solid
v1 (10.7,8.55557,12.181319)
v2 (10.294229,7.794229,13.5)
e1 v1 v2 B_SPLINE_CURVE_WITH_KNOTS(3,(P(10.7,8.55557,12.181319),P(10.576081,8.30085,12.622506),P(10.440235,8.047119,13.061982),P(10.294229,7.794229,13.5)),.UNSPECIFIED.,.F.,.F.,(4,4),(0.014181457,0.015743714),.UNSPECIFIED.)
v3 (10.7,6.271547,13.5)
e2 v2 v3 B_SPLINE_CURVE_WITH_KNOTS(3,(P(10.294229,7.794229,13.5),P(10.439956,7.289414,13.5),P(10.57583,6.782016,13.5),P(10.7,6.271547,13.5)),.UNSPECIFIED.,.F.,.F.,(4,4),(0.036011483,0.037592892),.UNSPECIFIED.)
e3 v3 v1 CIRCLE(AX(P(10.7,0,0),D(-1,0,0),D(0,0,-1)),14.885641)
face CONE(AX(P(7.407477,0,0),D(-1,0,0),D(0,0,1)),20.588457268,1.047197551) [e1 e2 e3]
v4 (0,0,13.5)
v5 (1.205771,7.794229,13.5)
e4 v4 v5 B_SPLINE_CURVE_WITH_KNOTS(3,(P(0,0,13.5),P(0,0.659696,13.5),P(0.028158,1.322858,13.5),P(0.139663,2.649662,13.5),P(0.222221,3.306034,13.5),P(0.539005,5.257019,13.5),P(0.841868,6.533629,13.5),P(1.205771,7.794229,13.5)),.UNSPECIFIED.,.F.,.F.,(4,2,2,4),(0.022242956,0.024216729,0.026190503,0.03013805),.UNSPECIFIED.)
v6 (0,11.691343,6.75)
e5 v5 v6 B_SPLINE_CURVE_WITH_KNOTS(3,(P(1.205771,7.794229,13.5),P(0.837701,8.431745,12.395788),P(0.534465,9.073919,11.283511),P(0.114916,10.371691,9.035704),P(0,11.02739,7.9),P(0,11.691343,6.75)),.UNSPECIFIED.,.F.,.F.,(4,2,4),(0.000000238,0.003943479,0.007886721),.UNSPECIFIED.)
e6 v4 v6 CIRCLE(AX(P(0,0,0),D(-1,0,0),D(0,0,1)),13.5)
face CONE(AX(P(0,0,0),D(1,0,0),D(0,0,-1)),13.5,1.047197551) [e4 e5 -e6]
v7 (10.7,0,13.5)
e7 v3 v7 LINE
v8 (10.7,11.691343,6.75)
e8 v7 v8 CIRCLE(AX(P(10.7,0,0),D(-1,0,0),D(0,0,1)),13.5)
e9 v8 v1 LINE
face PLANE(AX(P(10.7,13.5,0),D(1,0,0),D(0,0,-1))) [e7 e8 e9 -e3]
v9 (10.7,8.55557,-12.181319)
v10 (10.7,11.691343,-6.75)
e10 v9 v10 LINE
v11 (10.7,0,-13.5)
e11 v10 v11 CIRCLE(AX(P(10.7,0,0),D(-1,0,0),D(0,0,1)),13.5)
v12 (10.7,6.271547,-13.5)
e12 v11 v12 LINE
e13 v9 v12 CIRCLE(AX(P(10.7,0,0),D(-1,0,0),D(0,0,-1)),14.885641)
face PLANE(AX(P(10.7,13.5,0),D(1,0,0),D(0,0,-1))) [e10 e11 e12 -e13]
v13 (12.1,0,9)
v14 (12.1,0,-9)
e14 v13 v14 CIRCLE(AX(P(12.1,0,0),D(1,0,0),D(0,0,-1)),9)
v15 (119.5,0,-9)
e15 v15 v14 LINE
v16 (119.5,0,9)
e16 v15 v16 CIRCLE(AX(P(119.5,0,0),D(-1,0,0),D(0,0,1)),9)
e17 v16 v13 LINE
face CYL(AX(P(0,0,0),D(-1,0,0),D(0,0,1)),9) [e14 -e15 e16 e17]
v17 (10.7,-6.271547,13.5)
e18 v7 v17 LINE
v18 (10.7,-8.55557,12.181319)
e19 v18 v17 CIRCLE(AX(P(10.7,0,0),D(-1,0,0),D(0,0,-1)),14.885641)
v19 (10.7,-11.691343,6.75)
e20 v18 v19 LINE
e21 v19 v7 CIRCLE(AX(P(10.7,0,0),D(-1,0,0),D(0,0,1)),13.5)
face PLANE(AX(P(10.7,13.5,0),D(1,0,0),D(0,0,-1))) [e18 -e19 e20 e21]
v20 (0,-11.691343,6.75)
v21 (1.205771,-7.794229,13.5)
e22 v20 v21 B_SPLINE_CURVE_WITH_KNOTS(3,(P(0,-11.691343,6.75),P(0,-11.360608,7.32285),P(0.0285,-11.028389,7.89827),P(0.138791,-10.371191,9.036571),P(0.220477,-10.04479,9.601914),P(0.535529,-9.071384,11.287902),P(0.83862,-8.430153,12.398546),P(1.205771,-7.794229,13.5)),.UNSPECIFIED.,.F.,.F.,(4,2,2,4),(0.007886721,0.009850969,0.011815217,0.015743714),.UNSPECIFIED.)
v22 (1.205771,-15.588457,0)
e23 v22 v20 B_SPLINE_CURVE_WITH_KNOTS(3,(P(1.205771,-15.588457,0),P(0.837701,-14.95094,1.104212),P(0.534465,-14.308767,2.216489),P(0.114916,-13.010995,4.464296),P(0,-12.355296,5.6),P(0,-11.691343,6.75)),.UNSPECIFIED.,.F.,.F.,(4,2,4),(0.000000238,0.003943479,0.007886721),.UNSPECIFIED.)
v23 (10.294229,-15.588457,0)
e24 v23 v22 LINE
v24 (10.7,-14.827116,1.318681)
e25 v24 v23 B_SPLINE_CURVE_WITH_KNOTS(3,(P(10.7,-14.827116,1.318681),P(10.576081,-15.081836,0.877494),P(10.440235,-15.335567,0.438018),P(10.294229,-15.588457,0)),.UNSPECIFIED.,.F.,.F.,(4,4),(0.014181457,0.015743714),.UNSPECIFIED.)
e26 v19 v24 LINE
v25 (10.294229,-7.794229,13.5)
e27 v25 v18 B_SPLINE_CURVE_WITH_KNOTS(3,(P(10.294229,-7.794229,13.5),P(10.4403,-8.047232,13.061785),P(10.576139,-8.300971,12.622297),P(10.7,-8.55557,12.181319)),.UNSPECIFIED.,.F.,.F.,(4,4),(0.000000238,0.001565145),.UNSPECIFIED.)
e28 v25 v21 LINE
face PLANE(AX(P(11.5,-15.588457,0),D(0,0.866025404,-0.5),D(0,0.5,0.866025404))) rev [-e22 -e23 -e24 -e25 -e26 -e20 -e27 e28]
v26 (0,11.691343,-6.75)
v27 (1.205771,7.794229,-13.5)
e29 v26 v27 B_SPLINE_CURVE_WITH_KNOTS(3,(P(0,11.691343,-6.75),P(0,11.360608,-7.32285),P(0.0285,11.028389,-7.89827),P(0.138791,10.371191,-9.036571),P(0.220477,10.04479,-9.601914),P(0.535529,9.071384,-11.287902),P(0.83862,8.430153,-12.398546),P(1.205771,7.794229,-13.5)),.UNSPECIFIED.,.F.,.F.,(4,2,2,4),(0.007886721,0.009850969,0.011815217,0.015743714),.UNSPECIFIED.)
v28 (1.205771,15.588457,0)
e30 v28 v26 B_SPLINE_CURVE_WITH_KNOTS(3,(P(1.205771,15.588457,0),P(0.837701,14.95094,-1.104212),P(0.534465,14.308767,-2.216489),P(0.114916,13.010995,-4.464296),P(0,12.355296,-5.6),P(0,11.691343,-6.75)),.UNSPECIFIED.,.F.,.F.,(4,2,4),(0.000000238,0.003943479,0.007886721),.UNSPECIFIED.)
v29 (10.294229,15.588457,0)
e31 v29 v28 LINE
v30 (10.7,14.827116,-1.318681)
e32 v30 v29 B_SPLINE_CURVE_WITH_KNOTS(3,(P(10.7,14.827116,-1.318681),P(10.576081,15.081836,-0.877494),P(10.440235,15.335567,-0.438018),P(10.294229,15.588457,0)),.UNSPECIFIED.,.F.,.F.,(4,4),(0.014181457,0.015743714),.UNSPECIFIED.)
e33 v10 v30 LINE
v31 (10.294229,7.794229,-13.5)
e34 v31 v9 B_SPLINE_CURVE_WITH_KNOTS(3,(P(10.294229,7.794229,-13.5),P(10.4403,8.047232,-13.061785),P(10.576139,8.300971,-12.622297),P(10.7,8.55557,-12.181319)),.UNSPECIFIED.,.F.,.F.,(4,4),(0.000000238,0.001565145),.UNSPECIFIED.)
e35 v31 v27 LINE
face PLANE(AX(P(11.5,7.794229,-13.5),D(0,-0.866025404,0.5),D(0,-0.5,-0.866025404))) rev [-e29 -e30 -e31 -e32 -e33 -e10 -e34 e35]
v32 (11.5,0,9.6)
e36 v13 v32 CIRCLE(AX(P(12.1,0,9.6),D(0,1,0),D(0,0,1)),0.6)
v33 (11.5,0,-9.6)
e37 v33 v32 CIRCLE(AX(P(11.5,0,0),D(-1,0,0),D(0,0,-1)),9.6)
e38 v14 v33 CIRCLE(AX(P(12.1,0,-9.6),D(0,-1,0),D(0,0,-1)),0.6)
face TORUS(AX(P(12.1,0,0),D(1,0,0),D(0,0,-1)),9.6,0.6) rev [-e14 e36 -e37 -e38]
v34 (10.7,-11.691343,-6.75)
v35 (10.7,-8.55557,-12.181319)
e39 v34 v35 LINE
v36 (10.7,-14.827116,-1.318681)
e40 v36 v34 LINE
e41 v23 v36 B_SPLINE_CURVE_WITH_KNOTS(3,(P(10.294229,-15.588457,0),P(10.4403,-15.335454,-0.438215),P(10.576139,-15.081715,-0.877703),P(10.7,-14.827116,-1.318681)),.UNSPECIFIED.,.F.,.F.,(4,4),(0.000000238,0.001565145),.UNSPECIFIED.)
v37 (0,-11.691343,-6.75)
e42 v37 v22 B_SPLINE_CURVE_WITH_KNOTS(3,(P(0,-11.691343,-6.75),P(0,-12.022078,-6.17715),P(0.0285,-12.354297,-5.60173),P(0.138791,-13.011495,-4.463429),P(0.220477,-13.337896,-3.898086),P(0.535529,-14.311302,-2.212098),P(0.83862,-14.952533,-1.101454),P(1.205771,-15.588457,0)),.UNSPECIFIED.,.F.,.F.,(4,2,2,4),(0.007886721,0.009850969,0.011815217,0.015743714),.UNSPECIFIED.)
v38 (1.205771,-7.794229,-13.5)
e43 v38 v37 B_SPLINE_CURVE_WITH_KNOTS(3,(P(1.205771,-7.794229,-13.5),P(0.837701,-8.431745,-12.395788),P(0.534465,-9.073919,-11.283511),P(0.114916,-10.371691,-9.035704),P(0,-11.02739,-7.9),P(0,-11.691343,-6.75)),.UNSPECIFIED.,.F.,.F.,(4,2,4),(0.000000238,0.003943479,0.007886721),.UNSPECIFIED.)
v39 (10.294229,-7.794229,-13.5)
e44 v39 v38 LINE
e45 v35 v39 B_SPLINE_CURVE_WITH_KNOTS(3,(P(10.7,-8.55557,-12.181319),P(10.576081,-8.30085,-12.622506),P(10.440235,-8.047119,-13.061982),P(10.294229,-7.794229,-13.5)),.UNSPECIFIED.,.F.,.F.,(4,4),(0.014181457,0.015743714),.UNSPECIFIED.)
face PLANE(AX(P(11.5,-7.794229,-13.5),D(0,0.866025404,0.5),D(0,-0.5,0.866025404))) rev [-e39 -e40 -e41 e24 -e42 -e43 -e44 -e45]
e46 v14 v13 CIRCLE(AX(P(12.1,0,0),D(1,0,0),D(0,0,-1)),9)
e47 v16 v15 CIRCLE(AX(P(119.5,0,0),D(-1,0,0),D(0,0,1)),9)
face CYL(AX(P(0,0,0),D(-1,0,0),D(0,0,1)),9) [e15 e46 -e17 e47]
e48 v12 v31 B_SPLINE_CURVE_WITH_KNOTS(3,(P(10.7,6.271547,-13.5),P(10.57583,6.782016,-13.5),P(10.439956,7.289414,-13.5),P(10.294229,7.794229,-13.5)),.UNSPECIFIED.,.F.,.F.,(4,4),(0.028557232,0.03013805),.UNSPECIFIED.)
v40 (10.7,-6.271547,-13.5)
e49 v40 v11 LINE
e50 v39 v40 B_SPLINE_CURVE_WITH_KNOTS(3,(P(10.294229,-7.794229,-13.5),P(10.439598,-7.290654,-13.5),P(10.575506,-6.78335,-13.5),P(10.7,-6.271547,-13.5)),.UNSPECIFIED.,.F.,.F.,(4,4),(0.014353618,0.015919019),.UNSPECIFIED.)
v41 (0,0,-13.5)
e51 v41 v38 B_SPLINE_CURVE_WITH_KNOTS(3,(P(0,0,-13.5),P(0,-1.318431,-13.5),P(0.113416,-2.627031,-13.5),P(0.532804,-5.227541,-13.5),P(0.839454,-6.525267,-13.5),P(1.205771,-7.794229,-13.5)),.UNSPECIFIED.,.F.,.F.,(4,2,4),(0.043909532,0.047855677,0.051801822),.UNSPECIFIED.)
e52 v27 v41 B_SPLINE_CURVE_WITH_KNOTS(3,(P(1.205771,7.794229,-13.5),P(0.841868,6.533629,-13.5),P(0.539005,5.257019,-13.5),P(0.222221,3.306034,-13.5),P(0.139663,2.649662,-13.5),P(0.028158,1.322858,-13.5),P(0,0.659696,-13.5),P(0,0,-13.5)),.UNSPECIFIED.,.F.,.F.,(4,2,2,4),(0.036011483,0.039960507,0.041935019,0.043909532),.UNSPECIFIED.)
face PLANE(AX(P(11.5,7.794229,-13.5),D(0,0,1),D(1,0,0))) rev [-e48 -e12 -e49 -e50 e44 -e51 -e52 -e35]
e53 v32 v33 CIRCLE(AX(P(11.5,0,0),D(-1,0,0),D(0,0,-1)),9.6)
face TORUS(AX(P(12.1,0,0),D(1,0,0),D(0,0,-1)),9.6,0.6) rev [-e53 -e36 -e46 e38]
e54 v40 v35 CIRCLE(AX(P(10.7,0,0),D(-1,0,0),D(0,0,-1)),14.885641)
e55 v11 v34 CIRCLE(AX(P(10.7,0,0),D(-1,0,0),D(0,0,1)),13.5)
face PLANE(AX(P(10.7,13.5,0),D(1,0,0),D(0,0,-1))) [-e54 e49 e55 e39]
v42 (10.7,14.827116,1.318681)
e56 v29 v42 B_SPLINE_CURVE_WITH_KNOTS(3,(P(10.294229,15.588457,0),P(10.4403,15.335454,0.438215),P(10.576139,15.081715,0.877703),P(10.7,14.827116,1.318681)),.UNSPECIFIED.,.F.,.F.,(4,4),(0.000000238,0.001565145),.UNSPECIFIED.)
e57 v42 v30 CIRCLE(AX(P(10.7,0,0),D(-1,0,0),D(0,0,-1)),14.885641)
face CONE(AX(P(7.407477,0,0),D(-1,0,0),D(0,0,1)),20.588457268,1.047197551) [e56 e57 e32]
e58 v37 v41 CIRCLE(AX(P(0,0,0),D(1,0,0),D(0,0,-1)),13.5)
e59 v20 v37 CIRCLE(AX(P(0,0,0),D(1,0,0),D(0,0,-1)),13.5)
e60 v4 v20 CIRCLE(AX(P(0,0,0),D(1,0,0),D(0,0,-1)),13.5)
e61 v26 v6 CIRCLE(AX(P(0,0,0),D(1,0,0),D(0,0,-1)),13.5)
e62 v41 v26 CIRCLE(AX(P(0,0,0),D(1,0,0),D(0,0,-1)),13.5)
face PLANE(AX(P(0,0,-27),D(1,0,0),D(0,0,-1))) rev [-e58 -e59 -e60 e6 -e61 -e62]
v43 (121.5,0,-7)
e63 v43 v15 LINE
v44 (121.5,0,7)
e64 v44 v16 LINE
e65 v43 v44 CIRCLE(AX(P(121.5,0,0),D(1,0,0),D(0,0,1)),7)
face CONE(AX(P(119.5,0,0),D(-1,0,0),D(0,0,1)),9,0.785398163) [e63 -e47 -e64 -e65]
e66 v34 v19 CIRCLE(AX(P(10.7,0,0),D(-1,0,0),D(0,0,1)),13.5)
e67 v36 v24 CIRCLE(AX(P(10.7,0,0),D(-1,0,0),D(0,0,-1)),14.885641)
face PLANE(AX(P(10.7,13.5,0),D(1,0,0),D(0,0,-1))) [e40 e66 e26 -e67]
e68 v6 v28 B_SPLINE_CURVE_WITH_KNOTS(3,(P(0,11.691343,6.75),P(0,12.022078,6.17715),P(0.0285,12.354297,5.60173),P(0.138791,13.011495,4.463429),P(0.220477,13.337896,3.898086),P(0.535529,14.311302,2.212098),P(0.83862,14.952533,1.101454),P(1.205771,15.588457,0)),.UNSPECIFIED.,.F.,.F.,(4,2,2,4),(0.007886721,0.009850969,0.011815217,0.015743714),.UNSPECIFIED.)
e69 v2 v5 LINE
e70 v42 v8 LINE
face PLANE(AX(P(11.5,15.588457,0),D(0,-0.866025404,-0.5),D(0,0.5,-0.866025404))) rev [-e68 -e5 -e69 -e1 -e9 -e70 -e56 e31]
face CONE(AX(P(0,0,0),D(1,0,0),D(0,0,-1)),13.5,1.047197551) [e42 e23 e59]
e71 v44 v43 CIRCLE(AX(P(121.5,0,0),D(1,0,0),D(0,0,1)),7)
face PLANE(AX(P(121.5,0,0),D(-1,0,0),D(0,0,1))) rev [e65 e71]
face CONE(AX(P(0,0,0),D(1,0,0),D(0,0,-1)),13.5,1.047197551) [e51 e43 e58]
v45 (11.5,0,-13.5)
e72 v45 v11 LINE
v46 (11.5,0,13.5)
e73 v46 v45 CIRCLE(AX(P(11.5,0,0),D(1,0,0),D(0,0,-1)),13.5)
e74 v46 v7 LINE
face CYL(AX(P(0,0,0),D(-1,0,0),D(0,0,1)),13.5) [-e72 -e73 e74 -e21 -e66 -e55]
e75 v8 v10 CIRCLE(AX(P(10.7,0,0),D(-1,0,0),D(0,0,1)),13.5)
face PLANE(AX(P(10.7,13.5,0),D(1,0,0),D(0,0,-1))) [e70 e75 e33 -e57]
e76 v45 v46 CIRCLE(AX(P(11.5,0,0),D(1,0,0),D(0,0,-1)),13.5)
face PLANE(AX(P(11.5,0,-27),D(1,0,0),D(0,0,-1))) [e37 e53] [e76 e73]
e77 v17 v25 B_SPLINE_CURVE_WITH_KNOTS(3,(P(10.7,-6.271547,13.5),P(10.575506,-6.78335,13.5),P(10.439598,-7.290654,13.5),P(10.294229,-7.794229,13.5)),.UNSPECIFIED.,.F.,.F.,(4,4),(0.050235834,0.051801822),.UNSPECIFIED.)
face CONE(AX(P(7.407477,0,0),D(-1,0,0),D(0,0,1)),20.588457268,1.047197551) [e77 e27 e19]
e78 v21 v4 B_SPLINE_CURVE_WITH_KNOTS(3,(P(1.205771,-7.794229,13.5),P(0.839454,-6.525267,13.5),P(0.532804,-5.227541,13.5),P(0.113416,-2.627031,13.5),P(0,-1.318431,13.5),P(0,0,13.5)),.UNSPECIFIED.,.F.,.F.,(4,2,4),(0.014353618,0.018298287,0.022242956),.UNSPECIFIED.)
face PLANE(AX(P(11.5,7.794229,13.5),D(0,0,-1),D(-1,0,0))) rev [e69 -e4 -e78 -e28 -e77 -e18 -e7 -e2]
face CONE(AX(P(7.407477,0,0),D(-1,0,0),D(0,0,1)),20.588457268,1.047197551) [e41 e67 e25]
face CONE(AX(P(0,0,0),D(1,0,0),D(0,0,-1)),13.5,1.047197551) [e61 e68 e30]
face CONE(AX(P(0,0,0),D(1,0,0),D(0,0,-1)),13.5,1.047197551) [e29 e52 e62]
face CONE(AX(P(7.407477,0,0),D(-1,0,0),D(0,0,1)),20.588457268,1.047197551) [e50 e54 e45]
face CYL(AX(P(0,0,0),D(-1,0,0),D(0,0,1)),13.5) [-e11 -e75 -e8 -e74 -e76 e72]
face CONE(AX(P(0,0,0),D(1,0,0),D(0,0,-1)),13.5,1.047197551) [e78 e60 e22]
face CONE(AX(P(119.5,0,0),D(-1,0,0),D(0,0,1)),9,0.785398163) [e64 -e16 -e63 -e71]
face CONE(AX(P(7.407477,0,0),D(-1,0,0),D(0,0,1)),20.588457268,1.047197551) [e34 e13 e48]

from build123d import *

# Parameters (mm, degrees)
EXTRUDE_371_DEPTH = 11.5
SKETCH_4_W        = 0.8
SKETCH_4_H        = 12.088457268
CHAMFER_2038_SIZE = 2
FILLET_2080_R     = 0.6


with BuildPart() as part:
    # 草图1 → Extrude 371 (new body)
    with BuildSketch(Plane(origin=(0, 0, 0), x_dir=(0, 0, -1), z_dir=(1, 0, 0))):
        Polygon((13.5, 7.794228634), (13.5, -7.794228634), (0, -15.588457268), (-13.5, -7.794228634), (-13.5, 7.794228634), (0, 15.588457268), align=None)
    extrude(amount=EXTRUDE_371_DEPTH)

    # 草图2 → 凸台-旋转1 (revolve)
    with BuildSketch(Plane.XY, mode=Mode.PRIVATE) as revolve_1_sk:
        Polygon((0, 0), (121.5, 0), (121.5, 6.835), (121.5, 9), (27.8072, 9), (0, 9), align=None)
    revolve(revolve_1_sk.sketch.rotate(Axis((0, 0, 0), (1, 0, 0)), 90), axis=Axis((0, 0, 0), (1, 0, 0)))

    # 草图3 → 切除-旋转1 (revolve, cut)
    with BuildSketch(Plane.XY):
        Polygon((0, 13.5), (4.092522712, 20.588457268), (4.092522712, 25.588457268), (-10, 25.588457268), (-10, 13.5), align=None)
    revolve(axis=Axis((0, 0, 0), (1, 0, 0)), mode=Mode.SUBTRACT)

    # 草图5 → 切除-旋转2 (revolve, cut)
    with BuildSketch(Plane.XY):
        Polygon((11.5, 13.5), (7.407477288, 20.588457268), (7.407477288, 25.588457268), (17.407477288, 25.588457268), (17.407477288, 13.5), align=None)
    revolve(axis=Axis((0, 0, 0), (1, 0, 0)), mode=Mode.SUBTRACT)

    # 草图4 → 切除-旋转3 (revolve, cut)
    with BuildSketch(Plane.XY, mode=Mode.PRIVATE) as cut_revolve_3_sk:
        with Locations((11.1, 19.544228634)):
            Rectangle(SKETCH_4_W, SKETCH_4_H)
    revolve(cut_revolve_3_sk.sketch.rotate(Axis((0, 0, 0), (1, 0, 0)), 270), axis=Axis((0, 0, 0), (1, 0, 0)), mode=Mode.SUBTRACT)

    # Chamfer 2038
    chamfer_2038_edges = [part.edges().sort_by_distance(p)[0] for p in [
        (121.5, 0, -9),
    ]]
    chamfer(chamfer_2038_edges, length=CHAMFER_2038_SIZE)

    # Fillet 2080
    fillet_2080_edges = [part.edges().sort_by_distance(p)[0] for p in [
        (11.5, 0, -9),
    ]]
    fillet(fillet_2080_edges, radius=FILLET_2080_R)


solid = part.part
